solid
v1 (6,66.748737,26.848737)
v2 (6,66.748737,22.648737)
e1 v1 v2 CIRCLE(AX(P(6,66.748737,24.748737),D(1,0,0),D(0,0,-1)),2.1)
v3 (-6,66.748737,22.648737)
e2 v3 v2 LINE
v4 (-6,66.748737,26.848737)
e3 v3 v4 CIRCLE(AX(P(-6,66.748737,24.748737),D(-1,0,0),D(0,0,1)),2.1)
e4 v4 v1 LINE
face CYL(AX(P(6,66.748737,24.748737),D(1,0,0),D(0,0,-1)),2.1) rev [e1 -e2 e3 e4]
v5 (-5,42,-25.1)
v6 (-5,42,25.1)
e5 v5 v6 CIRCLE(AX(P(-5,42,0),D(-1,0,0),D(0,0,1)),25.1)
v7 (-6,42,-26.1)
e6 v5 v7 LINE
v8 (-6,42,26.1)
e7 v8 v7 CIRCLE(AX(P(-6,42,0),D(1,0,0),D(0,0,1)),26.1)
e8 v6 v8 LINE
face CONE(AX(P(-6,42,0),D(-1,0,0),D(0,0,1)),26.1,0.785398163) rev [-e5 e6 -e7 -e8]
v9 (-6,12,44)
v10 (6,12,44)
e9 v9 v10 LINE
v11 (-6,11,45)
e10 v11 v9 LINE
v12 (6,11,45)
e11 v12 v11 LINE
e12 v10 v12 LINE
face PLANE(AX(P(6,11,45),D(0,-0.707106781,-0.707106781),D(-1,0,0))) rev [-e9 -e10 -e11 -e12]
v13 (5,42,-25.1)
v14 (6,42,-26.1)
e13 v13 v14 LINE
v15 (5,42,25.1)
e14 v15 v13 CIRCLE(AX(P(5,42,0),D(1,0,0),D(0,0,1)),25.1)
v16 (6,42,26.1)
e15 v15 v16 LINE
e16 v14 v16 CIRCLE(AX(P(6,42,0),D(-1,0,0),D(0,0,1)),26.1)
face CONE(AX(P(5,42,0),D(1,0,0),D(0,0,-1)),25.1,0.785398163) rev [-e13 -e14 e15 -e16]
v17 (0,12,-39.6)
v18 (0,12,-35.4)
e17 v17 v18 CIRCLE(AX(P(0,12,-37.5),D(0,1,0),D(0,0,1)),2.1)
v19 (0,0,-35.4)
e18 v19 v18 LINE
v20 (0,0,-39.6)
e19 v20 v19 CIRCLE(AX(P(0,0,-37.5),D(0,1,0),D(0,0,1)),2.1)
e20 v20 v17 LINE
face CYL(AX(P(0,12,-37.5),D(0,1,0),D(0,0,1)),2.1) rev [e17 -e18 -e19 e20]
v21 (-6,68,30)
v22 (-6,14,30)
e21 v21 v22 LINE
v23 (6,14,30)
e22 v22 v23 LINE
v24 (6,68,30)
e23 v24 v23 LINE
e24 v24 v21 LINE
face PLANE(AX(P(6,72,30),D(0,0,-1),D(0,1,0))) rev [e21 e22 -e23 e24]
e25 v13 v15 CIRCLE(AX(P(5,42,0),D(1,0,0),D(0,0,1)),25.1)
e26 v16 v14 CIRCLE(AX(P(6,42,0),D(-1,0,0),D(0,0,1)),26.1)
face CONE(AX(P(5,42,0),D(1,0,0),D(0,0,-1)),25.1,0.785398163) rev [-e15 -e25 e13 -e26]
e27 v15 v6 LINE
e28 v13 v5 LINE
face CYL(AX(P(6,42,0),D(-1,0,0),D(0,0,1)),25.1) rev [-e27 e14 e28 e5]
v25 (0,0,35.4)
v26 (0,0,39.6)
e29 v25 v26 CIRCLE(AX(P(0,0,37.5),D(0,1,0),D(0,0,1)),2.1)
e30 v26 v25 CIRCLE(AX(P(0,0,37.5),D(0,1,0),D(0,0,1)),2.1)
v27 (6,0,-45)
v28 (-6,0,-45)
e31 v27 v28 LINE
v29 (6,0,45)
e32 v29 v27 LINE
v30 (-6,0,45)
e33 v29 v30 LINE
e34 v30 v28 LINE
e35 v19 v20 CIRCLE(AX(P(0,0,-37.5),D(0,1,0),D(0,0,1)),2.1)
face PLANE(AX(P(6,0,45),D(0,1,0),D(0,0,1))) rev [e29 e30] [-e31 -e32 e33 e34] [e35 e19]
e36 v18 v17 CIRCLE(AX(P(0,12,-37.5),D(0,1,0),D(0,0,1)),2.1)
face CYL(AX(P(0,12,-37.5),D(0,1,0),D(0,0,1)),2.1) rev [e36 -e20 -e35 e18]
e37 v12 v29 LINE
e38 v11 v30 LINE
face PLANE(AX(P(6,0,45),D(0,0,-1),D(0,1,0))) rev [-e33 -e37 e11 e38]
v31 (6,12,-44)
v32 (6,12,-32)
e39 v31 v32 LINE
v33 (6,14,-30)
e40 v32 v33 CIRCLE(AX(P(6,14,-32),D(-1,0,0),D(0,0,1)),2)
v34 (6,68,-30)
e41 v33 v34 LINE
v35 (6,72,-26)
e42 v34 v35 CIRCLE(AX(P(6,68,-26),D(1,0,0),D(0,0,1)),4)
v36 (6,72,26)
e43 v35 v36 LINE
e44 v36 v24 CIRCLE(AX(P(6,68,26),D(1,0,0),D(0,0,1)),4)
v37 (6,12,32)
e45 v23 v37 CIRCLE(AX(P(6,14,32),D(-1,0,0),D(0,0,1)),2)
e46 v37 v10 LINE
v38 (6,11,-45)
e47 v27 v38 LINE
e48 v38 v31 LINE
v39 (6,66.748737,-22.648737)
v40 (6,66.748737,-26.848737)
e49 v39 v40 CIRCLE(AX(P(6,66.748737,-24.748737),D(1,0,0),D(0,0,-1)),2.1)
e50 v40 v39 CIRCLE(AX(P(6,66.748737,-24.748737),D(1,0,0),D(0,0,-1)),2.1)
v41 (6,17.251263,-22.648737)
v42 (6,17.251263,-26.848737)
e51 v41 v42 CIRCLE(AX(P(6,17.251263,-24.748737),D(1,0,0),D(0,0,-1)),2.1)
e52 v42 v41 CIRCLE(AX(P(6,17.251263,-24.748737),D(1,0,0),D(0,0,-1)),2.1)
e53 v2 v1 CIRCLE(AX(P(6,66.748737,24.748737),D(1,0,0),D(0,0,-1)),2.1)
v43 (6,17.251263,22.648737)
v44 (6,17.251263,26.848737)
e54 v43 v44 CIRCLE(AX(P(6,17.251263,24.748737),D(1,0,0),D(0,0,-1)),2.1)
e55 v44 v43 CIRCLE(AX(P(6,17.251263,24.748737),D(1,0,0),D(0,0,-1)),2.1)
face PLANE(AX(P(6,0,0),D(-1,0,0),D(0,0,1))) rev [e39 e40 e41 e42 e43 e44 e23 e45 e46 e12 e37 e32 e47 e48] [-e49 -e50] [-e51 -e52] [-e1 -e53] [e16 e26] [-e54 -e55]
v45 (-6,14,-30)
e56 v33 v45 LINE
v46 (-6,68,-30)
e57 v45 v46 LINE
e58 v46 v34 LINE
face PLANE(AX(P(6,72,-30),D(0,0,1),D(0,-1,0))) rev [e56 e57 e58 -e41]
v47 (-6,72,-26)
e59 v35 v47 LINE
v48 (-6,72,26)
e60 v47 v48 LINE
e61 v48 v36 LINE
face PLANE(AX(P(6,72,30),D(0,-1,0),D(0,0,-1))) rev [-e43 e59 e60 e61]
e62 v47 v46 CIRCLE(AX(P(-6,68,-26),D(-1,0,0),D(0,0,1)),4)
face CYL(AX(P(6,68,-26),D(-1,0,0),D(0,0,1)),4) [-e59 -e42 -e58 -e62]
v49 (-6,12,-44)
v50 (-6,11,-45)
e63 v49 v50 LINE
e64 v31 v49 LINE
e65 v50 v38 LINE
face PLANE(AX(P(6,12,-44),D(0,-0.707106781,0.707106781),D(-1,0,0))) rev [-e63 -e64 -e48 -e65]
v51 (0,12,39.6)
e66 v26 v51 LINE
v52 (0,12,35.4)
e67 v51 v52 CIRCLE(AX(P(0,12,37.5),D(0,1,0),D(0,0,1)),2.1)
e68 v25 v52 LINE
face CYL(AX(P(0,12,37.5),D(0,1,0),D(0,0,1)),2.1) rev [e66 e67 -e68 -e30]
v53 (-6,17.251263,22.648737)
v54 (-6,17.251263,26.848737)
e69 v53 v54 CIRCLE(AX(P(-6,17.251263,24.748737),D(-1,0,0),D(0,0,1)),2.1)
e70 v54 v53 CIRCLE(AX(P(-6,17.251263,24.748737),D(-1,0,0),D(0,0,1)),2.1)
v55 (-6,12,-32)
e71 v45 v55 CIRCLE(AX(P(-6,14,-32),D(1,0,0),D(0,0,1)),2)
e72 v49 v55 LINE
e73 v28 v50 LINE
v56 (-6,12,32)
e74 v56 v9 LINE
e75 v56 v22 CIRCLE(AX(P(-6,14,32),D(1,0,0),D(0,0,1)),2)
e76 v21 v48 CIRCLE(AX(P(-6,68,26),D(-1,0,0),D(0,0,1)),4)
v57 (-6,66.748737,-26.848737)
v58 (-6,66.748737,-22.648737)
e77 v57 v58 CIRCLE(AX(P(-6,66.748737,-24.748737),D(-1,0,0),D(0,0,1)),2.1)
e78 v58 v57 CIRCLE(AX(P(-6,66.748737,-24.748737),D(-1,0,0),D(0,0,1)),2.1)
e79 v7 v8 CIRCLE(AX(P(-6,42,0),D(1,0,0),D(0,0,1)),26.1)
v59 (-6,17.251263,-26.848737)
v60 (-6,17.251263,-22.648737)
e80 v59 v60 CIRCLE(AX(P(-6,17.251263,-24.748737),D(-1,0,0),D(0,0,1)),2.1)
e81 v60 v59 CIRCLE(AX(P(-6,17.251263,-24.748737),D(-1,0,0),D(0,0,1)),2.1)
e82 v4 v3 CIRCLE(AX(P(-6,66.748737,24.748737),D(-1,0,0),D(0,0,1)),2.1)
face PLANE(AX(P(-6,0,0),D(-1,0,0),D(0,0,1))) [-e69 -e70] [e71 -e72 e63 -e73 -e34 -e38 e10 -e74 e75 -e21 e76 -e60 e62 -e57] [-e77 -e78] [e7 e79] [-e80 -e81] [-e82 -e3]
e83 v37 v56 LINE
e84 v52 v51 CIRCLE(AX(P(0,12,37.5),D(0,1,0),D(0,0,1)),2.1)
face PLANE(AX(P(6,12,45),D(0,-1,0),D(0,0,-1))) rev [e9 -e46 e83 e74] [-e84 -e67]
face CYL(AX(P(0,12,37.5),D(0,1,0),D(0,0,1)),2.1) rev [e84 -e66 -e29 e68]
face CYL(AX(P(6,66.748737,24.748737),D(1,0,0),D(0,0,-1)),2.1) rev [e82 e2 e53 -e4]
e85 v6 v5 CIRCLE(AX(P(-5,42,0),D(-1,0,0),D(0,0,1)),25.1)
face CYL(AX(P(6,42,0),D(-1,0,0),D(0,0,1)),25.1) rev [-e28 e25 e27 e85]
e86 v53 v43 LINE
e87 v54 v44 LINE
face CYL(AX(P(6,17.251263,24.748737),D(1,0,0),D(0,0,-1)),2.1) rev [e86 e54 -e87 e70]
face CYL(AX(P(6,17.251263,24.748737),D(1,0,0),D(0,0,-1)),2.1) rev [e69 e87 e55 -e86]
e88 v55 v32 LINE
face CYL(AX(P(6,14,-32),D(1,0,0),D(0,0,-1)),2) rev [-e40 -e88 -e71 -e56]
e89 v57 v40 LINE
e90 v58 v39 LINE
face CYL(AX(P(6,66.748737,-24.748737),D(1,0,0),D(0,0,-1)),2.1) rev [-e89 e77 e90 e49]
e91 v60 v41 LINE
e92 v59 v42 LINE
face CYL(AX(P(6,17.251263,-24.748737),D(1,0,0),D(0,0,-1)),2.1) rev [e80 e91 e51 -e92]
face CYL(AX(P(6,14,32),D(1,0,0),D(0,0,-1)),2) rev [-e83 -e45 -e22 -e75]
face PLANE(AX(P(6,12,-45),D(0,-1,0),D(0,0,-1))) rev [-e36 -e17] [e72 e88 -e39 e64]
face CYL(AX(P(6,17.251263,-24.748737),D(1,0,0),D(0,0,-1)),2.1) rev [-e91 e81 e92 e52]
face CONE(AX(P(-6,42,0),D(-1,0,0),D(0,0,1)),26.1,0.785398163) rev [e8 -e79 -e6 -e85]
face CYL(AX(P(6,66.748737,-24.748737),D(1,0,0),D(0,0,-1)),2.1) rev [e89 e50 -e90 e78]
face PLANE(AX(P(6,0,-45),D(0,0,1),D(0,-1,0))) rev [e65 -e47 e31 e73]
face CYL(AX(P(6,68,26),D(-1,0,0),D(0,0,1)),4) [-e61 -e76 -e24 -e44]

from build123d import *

# Parameters (mm, degrees)
SKETCH1_R             = 25.1
BOSS_EXTRUDE1_DEPTH   = 6
FILLET1_R             = 4
FILLET2_R             = 2
CHAMFER1_SIZE         = 1
M5_TAPPED_HOLE2_D     = 4.2
M5_TAPPED_HOLE1_D     = 4.2
M5_TAPPED_HOLE1_DEPTH = 14
M5_TAPPED_HOLE1_TIP   = 1.2618073
CHAMFER2_SIZE         = 1


with BuildPart() as part:
    # Sketch1 → Boss-Extrude1 (new, symmetric)
    with BuildSketch(Plane(origin=(0, 0, 0), x_dir=(0, 0, -1), z_dir=(1, 0, 0))):
        Polygon((-45, 0), (45, 0), (45, 12), (30, 12), (30, 72), (-30, 72), (-30, 12), (-45, 12), align=None)
        with Locations((0, 42)):
            Circle(SKETCH1_R, mode=Mode.SUBTRACT)
    extrude(amount=BOSS_EXTRUDE1_DEPTH, both=True)

    # Fillet1
    fillet1_edges = [part.edges().sort_by_distance(p)[0] for p in [
        (0, 72, 30),
        (0, 72, -30),
    ]]
    fillet(fillet1_edges, radius=FILLET1_R)

    # Fillet2
    fillet2_edges = [part.edges().sort_by_distance(p)[0] for p in [
        (0, 12, 30),
        (0, 12, -30),
    ]]
    fillet(fillet2_edges, radius=FILLET2_R)

    # Chamfer1
    chamfer1_edges = [part.edges().sort_by_distance(p)[0] for p in [
        (0, 12, 45),
        (0, 12, -45),
    ]]
    chamfer(chamfer1_edges, length=CHAMFER1_SIZE)

    # M5 Tapped Hole2 (through all)
    with Locations(Plane(origin=(0, 12, 0), x_dir=(1, 0, 0), z_dir=(0, 1, 0))):
        with Locations((0, -37.5), (0, 37.5)):
            Hole(M5_TAPPED_HOLE2_D / 2)

    # M5 Tapped Hole1
    with Locations(Plane(origin=(6, 0, 0), x_dir=(0, 0, -1), z_dir=(1, 0, 0))):
        with Locations((-24.748737342, 66.748737342), (24.748737342, 66.748737342), (24.748737342, 17.251262658), (-24.748737342, 17.251262658)):
            Hole(M5_TAPPED_HOLE1_D / 2, depth=M5_TAPPED_HOLE1_DEPTH)
            with Locations((0, 0, -(M5_TAPPED_HOLE1_DEPTH + M5_TAPPED_HOLE1_TIP / 2))):  # 118° drill point
                Cone(0, M5_TAPPED_HOLE1_D / 2, M5_TAPPED_HOLE1_TIP, mode=Mode.SUBTRACT)

    # Chamfer2
    chamfer2_edges = [part.edges().sort_by_distance(p)[0] for p in [
        (-6, 42, 25.1),
        (6, 42, 25.1),
    ]]
    chamfer(chamfer2_edges, length=CHAMFER2_SIZE)


solid = part.part
